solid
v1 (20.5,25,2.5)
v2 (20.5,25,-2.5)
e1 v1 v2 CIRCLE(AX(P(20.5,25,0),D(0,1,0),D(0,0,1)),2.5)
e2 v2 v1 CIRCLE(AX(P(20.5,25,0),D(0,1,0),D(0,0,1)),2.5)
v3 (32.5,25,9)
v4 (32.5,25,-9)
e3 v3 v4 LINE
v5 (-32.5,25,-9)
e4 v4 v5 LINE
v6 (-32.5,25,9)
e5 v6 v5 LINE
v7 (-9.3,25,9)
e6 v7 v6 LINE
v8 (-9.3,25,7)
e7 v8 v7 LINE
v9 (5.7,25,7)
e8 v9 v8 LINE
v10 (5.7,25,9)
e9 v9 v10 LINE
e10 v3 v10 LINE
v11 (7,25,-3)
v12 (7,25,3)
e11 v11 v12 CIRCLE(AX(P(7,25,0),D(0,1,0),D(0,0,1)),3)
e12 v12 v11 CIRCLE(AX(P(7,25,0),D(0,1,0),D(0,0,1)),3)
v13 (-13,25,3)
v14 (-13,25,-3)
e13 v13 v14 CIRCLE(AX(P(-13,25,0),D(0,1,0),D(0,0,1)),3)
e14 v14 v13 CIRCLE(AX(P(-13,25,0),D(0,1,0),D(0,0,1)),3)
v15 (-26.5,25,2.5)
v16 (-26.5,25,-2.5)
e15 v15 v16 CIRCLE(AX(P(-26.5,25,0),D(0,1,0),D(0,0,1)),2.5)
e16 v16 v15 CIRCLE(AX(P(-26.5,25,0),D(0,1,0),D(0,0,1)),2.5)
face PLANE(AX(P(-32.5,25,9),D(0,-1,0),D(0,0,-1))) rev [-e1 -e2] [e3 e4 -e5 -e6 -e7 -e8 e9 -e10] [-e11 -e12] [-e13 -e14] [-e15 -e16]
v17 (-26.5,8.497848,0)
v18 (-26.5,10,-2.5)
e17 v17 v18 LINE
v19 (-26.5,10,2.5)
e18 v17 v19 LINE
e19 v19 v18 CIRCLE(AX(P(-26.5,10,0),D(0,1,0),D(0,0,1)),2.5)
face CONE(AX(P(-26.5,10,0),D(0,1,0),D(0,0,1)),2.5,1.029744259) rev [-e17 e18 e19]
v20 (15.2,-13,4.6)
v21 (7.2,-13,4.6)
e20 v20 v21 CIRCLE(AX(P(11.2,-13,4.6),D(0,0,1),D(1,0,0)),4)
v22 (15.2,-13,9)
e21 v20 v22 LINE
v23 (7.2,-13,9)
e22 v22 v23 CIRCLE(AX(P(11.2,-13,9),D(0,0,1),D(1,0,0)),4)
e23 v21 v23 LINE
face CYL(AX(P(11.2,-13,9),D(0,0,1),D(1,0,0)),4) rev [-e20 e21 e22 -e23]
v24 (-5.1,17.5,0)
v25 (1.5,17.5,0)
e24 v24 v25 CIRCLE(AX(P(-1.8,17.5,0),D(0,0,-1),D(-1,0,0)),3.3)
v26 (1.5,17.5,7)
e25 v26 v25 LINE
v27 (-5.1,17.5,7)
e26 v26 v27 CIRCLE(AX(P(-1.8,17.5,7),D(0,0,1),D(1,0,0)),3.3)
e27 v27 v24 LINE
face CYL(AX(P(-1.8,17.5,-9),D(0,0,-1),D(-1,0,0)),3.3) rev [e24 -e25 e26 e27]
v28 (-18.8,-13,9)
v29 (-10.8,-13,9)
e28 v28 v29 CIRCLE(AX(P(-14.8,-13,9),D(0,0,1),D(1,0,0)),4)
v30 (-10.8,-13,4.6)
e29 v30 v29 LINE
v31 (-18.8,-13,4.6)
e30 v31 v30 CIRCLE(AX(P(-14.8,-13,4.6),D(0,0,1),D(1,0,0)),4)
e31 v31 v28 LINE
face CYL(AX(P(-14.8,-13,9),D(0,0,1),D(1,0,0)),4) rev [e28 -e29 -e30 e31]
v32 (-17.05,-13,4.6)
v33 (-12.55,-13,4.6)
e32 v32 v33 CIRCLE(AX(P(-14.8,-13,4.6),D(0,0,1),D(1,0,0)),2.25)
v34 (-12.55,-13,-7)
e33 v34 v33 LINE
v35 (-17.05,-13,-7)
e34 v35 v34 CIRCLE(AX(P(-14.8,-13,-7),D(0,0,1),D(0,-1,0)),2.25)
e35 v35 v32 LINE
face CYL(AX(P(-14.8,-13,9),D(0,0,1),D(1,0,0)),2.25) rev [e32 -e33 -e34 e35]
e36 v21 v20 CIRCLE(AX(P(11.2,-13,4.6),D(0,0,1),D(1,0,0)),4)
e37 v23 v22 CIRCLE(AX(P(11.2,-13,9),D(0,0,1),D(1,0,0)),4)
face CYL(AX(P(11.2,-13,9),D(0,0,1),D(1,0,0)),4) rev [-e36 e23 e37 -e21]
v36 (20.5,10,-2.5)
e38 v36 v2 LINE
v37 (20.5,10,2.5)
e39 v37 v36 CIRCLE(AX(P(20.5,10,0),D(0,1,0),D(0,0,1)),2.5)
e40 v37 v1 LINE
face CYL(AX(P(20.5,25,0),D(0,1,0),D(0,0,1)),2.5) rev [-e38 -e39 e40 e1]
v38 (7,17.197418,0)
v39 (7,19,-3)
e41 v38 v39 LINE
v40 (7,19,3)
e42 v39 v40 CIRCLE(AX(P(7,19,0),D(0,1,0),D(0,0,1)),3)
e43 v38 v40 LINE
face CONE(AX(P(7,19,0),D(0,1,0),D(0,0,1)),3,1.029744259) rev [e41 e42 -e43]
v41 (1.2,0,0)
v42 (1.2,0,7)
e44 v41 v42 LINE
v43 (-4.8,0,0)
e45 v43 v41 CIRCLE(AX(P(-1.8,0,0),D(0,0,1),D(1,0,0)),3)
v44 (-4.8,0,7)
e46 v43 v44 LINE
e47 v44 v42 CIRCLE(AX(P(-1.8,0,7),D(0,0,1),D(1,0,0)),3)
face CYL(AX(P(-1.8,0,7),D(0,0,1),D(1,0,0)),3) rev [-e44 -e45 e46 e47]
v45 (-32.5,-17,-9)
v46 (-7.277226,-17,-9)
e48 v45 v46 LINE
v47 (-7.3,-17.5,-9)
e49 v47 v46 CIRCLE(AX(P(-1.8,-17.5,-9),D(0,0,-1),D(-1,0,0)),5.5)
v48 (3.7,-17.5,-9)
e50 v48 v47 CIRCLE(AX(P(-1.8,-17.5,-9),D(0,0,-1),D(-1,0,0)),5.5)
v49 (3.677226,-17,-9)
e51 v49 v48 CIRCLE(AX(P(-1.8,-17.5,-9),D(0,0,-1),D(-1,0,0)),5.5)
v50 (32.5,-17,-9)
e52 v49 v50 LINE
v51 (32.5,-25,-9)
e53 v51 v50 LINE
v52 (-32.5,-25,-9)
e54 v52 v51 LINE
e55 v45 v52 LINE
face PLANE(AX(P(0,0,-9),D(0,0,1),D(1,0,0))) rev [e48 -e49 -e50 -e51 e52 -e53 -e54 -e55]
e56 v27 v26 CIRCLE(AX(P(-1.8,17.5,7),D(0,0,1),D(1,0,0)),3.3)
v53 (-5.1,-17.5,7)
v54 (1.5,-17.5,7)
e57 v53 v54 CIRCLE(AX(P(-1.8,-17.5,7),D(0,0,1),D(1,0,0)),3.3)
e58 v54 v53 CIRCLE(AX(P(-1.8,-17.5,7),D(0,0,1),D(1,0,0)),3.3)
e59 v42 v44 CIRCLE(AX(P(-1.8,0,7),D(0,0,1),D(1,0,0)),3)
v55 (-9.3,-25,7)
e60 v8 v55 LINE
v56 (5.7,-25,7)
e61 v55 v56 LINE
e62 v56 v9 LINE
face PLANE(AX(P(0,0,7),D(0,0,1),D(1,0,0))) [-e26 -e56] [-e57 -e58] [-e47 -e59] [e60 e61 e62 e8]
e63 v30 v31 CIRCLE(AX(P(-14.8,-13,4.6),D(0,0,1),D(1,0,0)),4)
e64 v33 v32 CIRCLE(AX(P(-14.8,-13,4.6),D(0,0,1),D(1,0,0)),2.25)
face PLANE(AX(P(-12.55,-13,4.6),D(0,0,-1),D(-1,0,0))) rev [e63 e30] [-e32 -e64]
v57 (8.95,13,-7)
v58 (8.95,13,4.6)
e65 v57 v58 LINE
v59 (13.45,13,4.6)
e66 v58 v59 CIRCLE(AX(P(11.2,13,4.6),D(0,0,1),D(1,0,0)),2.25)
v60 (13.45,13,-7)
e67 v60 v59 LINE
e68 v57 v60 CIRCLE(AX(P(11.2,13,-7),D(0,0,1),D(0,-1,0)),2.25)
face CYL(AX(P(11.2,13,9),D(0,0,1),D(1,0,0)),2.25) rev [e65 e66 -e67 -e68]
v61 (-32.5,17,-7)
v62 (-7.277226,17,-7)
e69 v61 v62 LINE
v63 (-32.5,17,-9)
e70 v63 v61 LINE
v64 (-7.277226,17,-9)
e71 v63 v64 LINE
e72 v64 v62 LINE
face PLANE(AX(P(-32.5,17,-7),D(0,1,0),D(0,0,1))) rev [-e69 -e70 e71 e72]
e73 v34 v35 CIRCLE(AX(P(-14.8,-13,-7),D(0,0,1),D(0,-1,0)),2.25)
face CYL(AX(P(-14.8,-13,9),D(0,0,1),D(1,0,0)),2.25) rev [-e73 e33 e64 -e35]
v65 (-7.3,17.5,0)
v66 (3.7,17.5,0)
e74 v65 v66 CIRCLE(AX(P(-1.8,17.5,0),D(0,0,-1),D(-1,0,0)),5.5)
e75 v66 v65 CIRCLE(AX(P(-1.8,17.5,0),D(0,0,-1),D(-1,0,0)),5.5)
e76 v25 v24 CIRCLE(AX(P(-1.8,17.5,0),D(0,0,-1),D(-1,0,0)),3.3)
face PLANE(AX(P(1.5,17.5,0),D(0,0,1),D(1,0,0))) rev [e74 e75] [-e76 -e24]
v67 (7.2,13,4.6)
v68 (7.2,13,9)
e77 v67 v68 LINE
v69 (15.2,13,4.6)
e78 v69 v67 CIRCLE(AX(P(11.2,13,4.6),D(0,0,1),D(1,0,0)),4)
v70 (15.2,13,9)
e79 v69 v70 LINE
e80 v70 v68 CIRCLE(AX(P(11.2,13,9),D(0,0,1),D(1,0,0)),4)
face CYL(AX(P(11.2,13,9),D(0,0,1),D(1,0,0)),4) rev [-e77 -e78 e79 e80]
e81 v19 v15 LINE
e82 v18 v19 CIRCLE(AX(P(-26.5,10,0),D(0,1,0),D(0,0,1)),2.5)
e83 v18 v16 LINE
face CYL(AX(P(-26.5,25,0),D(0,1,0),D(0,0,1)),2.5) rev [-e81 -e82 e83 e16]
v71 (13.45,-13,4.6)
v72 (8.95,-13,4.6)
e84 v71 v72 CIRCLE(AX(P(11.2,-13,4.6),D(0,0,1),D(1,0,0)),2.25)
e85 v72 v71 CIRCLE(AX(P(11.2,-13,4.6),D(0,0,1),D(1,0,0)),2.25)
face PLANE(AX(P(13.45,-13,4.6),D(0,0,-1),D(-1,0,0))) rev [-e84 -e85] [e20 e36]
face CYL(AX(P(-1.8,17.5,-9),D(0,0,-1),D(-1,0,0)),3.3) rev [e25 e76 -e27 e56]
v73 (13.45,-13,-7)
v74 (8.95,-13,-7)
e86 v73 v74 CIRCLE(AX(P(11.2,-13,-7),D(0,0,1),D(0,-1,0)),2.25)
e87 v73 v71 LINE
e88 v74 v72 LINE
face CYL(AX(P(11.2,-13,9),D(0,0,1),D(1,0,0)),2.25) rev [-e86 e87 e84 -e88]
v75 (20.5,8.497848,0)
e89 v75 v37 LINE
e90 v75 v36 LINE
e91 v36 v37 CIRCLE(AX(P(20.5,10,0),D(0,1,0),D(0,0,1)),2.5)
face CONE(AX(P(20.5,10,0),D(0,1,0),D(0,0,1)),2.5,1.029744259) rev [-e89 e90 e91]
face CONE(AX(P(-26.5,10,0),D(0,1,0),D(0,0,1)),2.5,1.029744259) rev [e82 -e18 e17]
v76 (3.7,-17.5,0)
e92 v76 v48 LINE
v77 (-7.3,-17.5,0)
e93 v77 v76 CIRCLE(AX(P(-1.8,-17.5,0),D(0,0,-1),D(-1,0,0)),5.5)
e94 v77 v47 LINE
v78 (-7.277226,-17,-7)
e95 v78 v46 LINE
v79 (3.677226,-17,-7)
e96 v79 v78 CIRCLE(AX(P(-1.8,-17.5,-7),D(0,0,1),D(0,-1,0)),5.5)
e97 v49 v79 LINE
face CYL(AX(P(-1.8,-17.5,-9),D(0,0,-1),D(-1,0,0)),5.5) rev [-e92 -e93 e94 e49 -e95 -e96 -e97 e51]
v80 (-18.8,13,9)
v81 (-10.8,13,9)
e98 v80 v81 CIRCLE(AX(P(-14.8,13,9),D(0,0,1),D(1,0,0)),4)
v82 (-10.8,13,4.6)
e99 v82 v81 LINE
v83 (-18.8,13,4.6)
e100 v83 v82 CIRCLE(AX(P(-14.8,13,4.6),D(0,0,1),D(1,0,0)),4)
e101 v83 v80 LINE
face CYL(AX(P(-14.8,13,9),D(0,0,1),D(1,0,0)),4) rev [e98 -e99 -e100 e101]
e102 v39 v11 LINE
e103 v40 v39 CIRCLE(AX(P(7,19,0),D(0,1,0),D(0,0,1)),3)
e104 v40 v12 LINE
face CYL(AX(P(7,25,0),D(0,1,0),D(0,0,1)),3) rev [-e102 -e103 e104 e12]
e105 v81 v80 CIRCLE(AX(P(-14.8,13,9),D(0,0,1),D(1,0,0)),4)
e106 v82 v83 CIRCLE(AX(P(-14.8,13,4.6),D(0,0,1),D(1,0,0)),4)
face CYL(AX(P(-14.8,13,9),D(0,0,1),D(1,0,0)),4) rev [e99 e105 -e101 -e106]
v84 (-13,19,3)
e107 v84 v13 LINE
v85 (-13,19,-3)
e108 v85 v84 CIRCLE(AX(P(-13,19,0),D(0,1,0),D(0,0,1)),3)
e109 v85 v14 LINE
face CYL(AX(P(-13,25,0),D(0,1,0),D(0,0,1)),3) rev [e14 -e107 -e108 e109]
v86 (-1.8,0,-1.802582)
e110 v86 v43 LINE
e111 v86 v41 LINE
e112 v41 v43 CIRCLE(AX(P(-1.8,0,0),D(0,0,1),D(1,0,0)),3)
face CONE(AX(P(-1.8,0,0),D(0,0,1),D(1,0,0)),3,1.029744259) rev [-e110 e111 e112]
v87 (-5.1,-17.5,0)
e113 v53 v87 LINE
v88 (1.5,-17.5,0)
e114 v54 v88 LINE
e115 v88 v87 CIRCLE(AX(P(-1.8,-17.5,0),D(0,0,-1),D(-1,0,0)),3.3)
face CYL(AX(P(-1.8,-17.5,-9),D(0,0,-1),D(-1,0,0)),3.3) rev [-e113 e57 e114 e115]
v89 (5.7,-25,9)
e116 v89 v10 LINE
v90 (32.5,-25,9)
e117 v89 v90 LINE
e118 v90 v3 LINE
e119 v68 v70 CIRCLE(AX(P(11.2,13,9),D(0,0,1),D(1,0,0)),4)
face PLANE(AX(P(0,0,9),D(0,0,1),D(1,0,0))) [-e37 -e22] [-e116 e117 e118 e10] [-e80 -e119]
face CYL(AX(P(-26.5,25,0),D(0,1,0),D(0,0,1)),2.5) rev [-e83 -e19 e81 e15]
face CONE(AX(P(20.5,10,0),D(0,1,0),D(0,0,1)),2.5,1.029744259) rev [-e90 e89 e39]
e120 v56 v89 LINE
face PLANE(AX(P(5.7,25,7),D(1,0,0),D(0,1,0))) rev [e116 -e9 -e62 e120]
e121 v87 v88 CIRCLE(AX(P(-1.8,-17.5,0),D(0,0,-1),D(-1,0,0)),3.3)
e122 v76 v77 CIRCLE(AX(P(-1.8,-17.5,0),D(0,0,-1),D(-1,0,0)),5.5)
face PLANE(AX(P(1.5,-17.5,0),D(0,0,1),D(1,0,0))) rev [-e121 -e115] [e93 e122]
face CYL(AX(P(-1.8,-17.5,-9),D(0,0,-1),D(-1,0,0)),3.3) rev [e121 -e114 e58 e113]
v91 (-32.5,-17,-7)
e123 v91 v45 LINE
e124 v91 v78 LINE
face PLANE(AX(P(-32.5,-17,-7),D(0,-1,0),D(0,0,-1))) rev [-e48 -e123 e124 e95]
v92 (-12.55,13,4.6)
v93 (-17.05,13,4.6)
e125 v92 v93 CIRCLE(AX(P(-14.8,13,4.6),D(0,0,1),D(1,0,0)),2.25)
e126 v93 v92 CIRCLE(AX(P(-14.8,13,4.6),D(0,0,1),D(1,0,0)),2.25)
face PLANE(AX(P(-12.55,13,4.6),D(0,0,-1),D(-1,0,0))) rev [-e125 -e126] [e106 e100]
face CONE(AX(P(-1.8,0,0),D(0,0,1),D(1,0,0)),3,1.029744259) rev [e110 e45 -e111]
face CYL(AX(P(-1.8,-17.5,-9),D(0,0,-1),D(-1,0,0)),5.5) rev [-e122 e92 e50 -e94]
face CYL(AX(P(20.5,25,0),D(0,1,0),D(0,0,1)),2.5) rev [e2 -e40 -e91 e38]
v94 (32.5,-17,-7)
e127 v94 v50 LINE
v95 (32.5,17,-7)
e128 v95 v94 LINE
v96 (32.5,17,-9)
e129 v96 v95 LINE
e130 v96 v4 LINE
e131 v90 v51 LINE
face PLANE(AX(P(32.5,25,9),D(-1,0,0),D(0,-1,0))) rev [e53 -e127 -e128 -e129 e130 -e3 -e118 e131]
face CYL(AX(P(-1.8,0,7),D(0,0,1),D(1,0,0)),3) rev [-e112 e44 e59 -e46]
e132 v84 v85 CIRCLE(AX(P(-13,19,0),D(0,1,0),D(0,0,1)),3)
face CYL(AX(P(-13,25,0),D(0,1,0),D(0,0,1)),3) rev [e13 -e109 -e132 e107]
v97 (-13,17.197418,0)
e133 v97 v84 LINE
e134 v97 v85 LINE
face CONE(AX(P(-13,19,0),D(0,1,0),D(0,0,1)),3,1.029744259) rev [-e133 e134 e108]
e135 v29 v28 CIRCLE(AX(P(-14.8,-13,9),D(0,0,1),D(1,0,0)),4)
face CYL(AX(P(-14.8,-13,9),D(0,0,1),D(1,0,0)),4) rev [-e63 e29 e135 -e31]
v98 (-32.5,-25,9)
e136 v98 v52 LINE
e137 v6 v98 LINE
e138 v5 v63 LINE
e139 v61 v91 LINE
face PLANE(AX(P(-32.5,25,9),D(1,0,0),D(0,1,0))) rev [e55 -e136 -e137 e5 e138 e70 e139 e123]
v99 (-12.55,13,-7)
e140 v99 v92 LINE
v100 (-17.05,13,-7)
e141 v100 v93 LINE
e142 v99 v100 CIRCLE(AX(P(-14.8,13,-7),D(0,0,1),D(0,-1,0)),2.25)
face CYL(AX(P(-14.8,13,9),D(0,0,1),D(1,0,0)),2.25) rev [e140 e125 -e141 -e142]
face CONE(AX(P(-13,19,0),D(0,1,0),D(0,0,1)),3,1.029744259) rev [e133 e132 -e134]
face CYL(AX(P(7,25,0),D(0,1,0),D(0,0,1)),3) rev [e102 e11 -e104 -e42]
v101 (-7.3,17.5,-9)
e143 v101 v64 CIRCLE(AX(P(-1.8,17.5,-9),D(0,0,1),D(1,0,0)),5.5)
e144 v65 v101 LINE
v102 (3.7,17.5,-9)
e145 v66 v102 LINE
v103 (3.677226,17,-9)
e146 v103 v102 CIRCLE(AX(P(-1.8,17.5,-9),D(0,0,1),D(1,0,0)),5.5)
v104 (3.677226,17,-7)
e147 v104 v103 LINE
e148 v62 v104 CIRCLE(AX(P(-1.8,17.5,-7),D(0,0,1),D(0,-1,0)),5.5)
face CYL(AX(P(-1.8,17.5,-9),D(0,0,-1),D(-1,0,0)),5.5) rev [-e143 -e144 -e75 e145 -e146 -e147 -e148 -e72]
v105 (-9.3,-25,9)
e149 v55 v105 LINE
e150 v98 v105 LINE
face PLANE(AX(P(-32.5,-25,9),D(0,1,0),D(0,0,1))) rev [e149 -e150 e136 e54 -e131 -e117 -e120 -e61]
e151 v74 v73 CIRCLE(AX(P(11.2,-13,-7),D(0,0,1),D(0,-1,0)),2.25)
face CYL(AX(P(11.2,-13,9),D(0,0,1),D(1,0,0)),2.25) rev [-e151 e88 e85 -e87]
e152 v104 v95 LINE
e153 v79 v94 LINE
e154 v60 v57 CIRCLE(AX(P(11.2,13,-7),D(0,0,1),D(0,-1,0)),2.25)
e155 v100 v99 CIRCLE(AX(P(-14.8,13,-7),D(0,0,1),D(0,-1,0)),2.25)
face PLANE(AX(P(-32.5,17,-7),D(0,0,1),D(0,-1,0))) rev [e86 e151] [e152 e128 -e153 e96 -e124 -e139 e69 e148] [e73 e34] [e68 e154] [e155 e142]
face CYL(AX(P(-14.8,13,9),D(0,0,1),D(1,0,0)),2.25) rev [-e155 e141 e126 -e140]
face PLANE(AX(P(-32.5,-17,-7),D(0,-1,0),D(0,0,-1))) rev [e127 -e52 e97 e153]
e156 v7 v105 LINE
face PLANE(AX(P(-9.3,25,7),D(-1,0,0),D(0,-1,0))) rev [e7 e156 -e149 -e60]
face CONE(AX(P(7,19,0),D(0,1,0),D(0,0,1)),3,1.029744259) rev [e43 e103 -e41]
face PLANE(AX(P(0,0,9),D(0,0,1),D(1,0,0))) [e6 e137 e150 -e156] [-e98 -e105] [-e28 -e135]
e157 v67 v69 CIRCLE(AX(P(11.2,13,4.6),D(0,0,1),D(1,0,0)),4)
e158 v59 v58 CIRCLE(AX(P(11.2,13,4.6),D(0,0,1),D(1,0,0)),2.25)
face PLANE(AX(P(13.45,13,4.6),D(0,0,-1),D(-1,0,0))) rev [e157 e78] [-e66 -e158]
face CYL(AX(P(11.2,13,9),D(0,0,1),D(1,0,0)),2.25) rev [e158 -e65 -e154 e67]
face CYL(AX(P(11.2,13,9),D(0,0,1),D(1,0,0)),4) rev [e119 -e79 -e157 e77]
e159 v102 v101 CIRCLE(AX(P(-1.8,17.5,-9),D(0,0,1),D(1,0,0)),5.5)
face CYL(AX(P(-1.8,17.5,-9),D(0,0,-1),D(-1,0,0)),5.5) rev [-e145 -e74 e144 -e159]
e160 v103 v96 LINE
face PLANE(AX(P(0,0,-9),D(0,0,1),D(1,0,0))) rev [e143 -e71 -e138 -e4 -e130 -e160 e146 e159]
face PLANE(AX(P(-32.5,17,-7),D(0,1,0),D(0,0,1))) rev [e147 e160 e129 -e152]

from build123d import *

# Parameters (mm, degrees)
SKETCH_1_W                   = 65
SKETCH_1_H                   = 50
EXTRUDE_1_DEPTH              = 9
SKETCH_4_W                   = 2
SKETCH_4_H                   = 34
CUT_EXTRUDE_1_DEPTH          = 71.221079456
HOLE_WIZARD_M4_1_D           = 4.5
HOLE_WIZARD_M4_1_CBORE_D     = 8
HOLE_WIZARD_M4_1_CBORE_DEPTH = 4.4
SKETCH_8_W                   = 15
SKETCH_8_H                   = 50
CUT_EXTRUDE_3_DEPTH          = 2
F_6_0MM_1_D                  = 6
F_6_0MM_1_DEPTH              = 7
F_6_0MM_1_TIP                = 1.802581857
HOLE_WIZARD_M6_2_D           = 6.6
HOLE_WIZARD_M6_2_CBORE_D     = 11
HOLE_WIZARD_M6_2_CBORE_DEPTH = 9
HOLE_WIZARD_M6_1_D           = 5
HOLE_WIZARD_M6_1_DEPTH       = 15
HOLE_WIZARD_M6_1_TIP         = 1.502151548
F_6_0MM_2_D                  = 6
F_6_0MM_2_DEPTH              = 6
F_6_0MM_2_TIP                = 1.802581857


with BuildPart() as part:
    # 草图1 → 凸台-拉伸1 (new, symmetric)
    with BuildSketch(Plane.XY):
        Rectangle(SKETCH_1_W, SKETCH_1_H)
    extrude(amount=EXTRUDE_1_DEPTH, both=True)

    # 草图4 → 切除-拉伸1 (cut, through all)
    with BuildSketch(Plane(origin=(32.5, 0, 0), x_dir=(0, 0, -1), z_dir=(1, 0, 0))):
        with Locations((8, 0)):
            Rectangle(SKETCH_4_W, SKETCH_4_H)
    extrude(amount=-CUT_EXTRUDE_1_DEPTH, mode=Mode.SUBTRACT)

    # Hole Wizard M4 _1 (through all)
    with Locations(Plane.XY.offset(9)):
        with Locations((11.2, -13), (-14.8, -13), (-14.8, 13), (11.2, 13)):
            CounterBoreHole(HOLE_WIZARD_M4_1_D / 2, HOLE_WIZARD_M4_1_CBORE_D / 2, HOLE_WIZARD_M4_1_CBORE_DEPTH)

    # 草图8 → 切除-拉伸3 (cut)
    with BuildSketch(Plane.XY.offset(9)):
        with Locations((-1.8, 0)):
            Rectangle(SKETCH_8_W, SKETCH_8_H)
    extrude(amount=-CUT_EXTRUDE_3_DEPTH, mode=Mode.SUBTRACT)

    # Ø6.0mm 暗销孔1
    with Locations(Plane.XY.offset(7)):
        with Locations((-1.8, 0)):
            Hole(F_6_0MM_1_D / 2, depth=F_6_0MM_1_DEPTH)
            with Locations((0, 0, -(F_6_0MM_1_DEPTH + F_6_0MM_1_TIP / 2))):  # 118° drill point
                Cone(0, F_6_0MM_1_D / 2, F_6_0MM_1_TIP, mode=Mode.SUBTRACT)

    # M6 六角凹头螺钉的柱形沉头孔2 (through all)
    with Locations(Plane(origin=(0, 0, -9), x_dir=(-1, 0, 0), z_dir=(0, 0, -1))):
        with Locations((1.8, 17.5), (1.8, -17.5)):
            CounterBoreHole(HOLE_WIZARD_M6_2_D / 2, HOLE_WIZARD_M6_2_CBORE_D / 2, HOLE_WIZARD_M6_2_CBORE_DEPTH)

    # M6 螺纹孔1
    with Locations(Plane(origin=(0, 25, 0), x_dir=(1, 0, 0), z_dir=(0, 1, 0))):
        with Locations((20.5, 0), (-26.5, 0)):
            Hole(HOLE_WIZARD_M6_1_D / 2, depth=HOLE_WIZARD_M6_1_DEPTH)
            with Locations((0, 0, -(HOLE_WIZARD_M6_1_DEPTH + HOLE_WIZARD_M6_1_TIP / 2))):  # 118° drill point
                Cone(0, HOLE_WIZARD_M6_1_D / 2, HOLE_WIZARD_M6_1_TIP, mode=Mode.SUBTRACT)

    # Ø6.0mm 暗销孔2
    with Locations(Plane(origin=(0, 25, 0), x_dir=(1, 0, 0), z_dir=(0, 1, 0))):
        with Locations((7, 0), (-13, 0)):
            Hole(F_6_0MM_2_D / 2, depth=F_6_0MM_2_DEPTH)
            with Locations((0, 0, -(F_6_0MM_2_DEPTH + F_6_0MM_2_TIP / 2))):  # 118° drill point
                Cone(0, F_6_0MM_2_D / 2, F_6_0MM_2_TIP, mode=Mode.SUBTRACT)


solid = part.part
